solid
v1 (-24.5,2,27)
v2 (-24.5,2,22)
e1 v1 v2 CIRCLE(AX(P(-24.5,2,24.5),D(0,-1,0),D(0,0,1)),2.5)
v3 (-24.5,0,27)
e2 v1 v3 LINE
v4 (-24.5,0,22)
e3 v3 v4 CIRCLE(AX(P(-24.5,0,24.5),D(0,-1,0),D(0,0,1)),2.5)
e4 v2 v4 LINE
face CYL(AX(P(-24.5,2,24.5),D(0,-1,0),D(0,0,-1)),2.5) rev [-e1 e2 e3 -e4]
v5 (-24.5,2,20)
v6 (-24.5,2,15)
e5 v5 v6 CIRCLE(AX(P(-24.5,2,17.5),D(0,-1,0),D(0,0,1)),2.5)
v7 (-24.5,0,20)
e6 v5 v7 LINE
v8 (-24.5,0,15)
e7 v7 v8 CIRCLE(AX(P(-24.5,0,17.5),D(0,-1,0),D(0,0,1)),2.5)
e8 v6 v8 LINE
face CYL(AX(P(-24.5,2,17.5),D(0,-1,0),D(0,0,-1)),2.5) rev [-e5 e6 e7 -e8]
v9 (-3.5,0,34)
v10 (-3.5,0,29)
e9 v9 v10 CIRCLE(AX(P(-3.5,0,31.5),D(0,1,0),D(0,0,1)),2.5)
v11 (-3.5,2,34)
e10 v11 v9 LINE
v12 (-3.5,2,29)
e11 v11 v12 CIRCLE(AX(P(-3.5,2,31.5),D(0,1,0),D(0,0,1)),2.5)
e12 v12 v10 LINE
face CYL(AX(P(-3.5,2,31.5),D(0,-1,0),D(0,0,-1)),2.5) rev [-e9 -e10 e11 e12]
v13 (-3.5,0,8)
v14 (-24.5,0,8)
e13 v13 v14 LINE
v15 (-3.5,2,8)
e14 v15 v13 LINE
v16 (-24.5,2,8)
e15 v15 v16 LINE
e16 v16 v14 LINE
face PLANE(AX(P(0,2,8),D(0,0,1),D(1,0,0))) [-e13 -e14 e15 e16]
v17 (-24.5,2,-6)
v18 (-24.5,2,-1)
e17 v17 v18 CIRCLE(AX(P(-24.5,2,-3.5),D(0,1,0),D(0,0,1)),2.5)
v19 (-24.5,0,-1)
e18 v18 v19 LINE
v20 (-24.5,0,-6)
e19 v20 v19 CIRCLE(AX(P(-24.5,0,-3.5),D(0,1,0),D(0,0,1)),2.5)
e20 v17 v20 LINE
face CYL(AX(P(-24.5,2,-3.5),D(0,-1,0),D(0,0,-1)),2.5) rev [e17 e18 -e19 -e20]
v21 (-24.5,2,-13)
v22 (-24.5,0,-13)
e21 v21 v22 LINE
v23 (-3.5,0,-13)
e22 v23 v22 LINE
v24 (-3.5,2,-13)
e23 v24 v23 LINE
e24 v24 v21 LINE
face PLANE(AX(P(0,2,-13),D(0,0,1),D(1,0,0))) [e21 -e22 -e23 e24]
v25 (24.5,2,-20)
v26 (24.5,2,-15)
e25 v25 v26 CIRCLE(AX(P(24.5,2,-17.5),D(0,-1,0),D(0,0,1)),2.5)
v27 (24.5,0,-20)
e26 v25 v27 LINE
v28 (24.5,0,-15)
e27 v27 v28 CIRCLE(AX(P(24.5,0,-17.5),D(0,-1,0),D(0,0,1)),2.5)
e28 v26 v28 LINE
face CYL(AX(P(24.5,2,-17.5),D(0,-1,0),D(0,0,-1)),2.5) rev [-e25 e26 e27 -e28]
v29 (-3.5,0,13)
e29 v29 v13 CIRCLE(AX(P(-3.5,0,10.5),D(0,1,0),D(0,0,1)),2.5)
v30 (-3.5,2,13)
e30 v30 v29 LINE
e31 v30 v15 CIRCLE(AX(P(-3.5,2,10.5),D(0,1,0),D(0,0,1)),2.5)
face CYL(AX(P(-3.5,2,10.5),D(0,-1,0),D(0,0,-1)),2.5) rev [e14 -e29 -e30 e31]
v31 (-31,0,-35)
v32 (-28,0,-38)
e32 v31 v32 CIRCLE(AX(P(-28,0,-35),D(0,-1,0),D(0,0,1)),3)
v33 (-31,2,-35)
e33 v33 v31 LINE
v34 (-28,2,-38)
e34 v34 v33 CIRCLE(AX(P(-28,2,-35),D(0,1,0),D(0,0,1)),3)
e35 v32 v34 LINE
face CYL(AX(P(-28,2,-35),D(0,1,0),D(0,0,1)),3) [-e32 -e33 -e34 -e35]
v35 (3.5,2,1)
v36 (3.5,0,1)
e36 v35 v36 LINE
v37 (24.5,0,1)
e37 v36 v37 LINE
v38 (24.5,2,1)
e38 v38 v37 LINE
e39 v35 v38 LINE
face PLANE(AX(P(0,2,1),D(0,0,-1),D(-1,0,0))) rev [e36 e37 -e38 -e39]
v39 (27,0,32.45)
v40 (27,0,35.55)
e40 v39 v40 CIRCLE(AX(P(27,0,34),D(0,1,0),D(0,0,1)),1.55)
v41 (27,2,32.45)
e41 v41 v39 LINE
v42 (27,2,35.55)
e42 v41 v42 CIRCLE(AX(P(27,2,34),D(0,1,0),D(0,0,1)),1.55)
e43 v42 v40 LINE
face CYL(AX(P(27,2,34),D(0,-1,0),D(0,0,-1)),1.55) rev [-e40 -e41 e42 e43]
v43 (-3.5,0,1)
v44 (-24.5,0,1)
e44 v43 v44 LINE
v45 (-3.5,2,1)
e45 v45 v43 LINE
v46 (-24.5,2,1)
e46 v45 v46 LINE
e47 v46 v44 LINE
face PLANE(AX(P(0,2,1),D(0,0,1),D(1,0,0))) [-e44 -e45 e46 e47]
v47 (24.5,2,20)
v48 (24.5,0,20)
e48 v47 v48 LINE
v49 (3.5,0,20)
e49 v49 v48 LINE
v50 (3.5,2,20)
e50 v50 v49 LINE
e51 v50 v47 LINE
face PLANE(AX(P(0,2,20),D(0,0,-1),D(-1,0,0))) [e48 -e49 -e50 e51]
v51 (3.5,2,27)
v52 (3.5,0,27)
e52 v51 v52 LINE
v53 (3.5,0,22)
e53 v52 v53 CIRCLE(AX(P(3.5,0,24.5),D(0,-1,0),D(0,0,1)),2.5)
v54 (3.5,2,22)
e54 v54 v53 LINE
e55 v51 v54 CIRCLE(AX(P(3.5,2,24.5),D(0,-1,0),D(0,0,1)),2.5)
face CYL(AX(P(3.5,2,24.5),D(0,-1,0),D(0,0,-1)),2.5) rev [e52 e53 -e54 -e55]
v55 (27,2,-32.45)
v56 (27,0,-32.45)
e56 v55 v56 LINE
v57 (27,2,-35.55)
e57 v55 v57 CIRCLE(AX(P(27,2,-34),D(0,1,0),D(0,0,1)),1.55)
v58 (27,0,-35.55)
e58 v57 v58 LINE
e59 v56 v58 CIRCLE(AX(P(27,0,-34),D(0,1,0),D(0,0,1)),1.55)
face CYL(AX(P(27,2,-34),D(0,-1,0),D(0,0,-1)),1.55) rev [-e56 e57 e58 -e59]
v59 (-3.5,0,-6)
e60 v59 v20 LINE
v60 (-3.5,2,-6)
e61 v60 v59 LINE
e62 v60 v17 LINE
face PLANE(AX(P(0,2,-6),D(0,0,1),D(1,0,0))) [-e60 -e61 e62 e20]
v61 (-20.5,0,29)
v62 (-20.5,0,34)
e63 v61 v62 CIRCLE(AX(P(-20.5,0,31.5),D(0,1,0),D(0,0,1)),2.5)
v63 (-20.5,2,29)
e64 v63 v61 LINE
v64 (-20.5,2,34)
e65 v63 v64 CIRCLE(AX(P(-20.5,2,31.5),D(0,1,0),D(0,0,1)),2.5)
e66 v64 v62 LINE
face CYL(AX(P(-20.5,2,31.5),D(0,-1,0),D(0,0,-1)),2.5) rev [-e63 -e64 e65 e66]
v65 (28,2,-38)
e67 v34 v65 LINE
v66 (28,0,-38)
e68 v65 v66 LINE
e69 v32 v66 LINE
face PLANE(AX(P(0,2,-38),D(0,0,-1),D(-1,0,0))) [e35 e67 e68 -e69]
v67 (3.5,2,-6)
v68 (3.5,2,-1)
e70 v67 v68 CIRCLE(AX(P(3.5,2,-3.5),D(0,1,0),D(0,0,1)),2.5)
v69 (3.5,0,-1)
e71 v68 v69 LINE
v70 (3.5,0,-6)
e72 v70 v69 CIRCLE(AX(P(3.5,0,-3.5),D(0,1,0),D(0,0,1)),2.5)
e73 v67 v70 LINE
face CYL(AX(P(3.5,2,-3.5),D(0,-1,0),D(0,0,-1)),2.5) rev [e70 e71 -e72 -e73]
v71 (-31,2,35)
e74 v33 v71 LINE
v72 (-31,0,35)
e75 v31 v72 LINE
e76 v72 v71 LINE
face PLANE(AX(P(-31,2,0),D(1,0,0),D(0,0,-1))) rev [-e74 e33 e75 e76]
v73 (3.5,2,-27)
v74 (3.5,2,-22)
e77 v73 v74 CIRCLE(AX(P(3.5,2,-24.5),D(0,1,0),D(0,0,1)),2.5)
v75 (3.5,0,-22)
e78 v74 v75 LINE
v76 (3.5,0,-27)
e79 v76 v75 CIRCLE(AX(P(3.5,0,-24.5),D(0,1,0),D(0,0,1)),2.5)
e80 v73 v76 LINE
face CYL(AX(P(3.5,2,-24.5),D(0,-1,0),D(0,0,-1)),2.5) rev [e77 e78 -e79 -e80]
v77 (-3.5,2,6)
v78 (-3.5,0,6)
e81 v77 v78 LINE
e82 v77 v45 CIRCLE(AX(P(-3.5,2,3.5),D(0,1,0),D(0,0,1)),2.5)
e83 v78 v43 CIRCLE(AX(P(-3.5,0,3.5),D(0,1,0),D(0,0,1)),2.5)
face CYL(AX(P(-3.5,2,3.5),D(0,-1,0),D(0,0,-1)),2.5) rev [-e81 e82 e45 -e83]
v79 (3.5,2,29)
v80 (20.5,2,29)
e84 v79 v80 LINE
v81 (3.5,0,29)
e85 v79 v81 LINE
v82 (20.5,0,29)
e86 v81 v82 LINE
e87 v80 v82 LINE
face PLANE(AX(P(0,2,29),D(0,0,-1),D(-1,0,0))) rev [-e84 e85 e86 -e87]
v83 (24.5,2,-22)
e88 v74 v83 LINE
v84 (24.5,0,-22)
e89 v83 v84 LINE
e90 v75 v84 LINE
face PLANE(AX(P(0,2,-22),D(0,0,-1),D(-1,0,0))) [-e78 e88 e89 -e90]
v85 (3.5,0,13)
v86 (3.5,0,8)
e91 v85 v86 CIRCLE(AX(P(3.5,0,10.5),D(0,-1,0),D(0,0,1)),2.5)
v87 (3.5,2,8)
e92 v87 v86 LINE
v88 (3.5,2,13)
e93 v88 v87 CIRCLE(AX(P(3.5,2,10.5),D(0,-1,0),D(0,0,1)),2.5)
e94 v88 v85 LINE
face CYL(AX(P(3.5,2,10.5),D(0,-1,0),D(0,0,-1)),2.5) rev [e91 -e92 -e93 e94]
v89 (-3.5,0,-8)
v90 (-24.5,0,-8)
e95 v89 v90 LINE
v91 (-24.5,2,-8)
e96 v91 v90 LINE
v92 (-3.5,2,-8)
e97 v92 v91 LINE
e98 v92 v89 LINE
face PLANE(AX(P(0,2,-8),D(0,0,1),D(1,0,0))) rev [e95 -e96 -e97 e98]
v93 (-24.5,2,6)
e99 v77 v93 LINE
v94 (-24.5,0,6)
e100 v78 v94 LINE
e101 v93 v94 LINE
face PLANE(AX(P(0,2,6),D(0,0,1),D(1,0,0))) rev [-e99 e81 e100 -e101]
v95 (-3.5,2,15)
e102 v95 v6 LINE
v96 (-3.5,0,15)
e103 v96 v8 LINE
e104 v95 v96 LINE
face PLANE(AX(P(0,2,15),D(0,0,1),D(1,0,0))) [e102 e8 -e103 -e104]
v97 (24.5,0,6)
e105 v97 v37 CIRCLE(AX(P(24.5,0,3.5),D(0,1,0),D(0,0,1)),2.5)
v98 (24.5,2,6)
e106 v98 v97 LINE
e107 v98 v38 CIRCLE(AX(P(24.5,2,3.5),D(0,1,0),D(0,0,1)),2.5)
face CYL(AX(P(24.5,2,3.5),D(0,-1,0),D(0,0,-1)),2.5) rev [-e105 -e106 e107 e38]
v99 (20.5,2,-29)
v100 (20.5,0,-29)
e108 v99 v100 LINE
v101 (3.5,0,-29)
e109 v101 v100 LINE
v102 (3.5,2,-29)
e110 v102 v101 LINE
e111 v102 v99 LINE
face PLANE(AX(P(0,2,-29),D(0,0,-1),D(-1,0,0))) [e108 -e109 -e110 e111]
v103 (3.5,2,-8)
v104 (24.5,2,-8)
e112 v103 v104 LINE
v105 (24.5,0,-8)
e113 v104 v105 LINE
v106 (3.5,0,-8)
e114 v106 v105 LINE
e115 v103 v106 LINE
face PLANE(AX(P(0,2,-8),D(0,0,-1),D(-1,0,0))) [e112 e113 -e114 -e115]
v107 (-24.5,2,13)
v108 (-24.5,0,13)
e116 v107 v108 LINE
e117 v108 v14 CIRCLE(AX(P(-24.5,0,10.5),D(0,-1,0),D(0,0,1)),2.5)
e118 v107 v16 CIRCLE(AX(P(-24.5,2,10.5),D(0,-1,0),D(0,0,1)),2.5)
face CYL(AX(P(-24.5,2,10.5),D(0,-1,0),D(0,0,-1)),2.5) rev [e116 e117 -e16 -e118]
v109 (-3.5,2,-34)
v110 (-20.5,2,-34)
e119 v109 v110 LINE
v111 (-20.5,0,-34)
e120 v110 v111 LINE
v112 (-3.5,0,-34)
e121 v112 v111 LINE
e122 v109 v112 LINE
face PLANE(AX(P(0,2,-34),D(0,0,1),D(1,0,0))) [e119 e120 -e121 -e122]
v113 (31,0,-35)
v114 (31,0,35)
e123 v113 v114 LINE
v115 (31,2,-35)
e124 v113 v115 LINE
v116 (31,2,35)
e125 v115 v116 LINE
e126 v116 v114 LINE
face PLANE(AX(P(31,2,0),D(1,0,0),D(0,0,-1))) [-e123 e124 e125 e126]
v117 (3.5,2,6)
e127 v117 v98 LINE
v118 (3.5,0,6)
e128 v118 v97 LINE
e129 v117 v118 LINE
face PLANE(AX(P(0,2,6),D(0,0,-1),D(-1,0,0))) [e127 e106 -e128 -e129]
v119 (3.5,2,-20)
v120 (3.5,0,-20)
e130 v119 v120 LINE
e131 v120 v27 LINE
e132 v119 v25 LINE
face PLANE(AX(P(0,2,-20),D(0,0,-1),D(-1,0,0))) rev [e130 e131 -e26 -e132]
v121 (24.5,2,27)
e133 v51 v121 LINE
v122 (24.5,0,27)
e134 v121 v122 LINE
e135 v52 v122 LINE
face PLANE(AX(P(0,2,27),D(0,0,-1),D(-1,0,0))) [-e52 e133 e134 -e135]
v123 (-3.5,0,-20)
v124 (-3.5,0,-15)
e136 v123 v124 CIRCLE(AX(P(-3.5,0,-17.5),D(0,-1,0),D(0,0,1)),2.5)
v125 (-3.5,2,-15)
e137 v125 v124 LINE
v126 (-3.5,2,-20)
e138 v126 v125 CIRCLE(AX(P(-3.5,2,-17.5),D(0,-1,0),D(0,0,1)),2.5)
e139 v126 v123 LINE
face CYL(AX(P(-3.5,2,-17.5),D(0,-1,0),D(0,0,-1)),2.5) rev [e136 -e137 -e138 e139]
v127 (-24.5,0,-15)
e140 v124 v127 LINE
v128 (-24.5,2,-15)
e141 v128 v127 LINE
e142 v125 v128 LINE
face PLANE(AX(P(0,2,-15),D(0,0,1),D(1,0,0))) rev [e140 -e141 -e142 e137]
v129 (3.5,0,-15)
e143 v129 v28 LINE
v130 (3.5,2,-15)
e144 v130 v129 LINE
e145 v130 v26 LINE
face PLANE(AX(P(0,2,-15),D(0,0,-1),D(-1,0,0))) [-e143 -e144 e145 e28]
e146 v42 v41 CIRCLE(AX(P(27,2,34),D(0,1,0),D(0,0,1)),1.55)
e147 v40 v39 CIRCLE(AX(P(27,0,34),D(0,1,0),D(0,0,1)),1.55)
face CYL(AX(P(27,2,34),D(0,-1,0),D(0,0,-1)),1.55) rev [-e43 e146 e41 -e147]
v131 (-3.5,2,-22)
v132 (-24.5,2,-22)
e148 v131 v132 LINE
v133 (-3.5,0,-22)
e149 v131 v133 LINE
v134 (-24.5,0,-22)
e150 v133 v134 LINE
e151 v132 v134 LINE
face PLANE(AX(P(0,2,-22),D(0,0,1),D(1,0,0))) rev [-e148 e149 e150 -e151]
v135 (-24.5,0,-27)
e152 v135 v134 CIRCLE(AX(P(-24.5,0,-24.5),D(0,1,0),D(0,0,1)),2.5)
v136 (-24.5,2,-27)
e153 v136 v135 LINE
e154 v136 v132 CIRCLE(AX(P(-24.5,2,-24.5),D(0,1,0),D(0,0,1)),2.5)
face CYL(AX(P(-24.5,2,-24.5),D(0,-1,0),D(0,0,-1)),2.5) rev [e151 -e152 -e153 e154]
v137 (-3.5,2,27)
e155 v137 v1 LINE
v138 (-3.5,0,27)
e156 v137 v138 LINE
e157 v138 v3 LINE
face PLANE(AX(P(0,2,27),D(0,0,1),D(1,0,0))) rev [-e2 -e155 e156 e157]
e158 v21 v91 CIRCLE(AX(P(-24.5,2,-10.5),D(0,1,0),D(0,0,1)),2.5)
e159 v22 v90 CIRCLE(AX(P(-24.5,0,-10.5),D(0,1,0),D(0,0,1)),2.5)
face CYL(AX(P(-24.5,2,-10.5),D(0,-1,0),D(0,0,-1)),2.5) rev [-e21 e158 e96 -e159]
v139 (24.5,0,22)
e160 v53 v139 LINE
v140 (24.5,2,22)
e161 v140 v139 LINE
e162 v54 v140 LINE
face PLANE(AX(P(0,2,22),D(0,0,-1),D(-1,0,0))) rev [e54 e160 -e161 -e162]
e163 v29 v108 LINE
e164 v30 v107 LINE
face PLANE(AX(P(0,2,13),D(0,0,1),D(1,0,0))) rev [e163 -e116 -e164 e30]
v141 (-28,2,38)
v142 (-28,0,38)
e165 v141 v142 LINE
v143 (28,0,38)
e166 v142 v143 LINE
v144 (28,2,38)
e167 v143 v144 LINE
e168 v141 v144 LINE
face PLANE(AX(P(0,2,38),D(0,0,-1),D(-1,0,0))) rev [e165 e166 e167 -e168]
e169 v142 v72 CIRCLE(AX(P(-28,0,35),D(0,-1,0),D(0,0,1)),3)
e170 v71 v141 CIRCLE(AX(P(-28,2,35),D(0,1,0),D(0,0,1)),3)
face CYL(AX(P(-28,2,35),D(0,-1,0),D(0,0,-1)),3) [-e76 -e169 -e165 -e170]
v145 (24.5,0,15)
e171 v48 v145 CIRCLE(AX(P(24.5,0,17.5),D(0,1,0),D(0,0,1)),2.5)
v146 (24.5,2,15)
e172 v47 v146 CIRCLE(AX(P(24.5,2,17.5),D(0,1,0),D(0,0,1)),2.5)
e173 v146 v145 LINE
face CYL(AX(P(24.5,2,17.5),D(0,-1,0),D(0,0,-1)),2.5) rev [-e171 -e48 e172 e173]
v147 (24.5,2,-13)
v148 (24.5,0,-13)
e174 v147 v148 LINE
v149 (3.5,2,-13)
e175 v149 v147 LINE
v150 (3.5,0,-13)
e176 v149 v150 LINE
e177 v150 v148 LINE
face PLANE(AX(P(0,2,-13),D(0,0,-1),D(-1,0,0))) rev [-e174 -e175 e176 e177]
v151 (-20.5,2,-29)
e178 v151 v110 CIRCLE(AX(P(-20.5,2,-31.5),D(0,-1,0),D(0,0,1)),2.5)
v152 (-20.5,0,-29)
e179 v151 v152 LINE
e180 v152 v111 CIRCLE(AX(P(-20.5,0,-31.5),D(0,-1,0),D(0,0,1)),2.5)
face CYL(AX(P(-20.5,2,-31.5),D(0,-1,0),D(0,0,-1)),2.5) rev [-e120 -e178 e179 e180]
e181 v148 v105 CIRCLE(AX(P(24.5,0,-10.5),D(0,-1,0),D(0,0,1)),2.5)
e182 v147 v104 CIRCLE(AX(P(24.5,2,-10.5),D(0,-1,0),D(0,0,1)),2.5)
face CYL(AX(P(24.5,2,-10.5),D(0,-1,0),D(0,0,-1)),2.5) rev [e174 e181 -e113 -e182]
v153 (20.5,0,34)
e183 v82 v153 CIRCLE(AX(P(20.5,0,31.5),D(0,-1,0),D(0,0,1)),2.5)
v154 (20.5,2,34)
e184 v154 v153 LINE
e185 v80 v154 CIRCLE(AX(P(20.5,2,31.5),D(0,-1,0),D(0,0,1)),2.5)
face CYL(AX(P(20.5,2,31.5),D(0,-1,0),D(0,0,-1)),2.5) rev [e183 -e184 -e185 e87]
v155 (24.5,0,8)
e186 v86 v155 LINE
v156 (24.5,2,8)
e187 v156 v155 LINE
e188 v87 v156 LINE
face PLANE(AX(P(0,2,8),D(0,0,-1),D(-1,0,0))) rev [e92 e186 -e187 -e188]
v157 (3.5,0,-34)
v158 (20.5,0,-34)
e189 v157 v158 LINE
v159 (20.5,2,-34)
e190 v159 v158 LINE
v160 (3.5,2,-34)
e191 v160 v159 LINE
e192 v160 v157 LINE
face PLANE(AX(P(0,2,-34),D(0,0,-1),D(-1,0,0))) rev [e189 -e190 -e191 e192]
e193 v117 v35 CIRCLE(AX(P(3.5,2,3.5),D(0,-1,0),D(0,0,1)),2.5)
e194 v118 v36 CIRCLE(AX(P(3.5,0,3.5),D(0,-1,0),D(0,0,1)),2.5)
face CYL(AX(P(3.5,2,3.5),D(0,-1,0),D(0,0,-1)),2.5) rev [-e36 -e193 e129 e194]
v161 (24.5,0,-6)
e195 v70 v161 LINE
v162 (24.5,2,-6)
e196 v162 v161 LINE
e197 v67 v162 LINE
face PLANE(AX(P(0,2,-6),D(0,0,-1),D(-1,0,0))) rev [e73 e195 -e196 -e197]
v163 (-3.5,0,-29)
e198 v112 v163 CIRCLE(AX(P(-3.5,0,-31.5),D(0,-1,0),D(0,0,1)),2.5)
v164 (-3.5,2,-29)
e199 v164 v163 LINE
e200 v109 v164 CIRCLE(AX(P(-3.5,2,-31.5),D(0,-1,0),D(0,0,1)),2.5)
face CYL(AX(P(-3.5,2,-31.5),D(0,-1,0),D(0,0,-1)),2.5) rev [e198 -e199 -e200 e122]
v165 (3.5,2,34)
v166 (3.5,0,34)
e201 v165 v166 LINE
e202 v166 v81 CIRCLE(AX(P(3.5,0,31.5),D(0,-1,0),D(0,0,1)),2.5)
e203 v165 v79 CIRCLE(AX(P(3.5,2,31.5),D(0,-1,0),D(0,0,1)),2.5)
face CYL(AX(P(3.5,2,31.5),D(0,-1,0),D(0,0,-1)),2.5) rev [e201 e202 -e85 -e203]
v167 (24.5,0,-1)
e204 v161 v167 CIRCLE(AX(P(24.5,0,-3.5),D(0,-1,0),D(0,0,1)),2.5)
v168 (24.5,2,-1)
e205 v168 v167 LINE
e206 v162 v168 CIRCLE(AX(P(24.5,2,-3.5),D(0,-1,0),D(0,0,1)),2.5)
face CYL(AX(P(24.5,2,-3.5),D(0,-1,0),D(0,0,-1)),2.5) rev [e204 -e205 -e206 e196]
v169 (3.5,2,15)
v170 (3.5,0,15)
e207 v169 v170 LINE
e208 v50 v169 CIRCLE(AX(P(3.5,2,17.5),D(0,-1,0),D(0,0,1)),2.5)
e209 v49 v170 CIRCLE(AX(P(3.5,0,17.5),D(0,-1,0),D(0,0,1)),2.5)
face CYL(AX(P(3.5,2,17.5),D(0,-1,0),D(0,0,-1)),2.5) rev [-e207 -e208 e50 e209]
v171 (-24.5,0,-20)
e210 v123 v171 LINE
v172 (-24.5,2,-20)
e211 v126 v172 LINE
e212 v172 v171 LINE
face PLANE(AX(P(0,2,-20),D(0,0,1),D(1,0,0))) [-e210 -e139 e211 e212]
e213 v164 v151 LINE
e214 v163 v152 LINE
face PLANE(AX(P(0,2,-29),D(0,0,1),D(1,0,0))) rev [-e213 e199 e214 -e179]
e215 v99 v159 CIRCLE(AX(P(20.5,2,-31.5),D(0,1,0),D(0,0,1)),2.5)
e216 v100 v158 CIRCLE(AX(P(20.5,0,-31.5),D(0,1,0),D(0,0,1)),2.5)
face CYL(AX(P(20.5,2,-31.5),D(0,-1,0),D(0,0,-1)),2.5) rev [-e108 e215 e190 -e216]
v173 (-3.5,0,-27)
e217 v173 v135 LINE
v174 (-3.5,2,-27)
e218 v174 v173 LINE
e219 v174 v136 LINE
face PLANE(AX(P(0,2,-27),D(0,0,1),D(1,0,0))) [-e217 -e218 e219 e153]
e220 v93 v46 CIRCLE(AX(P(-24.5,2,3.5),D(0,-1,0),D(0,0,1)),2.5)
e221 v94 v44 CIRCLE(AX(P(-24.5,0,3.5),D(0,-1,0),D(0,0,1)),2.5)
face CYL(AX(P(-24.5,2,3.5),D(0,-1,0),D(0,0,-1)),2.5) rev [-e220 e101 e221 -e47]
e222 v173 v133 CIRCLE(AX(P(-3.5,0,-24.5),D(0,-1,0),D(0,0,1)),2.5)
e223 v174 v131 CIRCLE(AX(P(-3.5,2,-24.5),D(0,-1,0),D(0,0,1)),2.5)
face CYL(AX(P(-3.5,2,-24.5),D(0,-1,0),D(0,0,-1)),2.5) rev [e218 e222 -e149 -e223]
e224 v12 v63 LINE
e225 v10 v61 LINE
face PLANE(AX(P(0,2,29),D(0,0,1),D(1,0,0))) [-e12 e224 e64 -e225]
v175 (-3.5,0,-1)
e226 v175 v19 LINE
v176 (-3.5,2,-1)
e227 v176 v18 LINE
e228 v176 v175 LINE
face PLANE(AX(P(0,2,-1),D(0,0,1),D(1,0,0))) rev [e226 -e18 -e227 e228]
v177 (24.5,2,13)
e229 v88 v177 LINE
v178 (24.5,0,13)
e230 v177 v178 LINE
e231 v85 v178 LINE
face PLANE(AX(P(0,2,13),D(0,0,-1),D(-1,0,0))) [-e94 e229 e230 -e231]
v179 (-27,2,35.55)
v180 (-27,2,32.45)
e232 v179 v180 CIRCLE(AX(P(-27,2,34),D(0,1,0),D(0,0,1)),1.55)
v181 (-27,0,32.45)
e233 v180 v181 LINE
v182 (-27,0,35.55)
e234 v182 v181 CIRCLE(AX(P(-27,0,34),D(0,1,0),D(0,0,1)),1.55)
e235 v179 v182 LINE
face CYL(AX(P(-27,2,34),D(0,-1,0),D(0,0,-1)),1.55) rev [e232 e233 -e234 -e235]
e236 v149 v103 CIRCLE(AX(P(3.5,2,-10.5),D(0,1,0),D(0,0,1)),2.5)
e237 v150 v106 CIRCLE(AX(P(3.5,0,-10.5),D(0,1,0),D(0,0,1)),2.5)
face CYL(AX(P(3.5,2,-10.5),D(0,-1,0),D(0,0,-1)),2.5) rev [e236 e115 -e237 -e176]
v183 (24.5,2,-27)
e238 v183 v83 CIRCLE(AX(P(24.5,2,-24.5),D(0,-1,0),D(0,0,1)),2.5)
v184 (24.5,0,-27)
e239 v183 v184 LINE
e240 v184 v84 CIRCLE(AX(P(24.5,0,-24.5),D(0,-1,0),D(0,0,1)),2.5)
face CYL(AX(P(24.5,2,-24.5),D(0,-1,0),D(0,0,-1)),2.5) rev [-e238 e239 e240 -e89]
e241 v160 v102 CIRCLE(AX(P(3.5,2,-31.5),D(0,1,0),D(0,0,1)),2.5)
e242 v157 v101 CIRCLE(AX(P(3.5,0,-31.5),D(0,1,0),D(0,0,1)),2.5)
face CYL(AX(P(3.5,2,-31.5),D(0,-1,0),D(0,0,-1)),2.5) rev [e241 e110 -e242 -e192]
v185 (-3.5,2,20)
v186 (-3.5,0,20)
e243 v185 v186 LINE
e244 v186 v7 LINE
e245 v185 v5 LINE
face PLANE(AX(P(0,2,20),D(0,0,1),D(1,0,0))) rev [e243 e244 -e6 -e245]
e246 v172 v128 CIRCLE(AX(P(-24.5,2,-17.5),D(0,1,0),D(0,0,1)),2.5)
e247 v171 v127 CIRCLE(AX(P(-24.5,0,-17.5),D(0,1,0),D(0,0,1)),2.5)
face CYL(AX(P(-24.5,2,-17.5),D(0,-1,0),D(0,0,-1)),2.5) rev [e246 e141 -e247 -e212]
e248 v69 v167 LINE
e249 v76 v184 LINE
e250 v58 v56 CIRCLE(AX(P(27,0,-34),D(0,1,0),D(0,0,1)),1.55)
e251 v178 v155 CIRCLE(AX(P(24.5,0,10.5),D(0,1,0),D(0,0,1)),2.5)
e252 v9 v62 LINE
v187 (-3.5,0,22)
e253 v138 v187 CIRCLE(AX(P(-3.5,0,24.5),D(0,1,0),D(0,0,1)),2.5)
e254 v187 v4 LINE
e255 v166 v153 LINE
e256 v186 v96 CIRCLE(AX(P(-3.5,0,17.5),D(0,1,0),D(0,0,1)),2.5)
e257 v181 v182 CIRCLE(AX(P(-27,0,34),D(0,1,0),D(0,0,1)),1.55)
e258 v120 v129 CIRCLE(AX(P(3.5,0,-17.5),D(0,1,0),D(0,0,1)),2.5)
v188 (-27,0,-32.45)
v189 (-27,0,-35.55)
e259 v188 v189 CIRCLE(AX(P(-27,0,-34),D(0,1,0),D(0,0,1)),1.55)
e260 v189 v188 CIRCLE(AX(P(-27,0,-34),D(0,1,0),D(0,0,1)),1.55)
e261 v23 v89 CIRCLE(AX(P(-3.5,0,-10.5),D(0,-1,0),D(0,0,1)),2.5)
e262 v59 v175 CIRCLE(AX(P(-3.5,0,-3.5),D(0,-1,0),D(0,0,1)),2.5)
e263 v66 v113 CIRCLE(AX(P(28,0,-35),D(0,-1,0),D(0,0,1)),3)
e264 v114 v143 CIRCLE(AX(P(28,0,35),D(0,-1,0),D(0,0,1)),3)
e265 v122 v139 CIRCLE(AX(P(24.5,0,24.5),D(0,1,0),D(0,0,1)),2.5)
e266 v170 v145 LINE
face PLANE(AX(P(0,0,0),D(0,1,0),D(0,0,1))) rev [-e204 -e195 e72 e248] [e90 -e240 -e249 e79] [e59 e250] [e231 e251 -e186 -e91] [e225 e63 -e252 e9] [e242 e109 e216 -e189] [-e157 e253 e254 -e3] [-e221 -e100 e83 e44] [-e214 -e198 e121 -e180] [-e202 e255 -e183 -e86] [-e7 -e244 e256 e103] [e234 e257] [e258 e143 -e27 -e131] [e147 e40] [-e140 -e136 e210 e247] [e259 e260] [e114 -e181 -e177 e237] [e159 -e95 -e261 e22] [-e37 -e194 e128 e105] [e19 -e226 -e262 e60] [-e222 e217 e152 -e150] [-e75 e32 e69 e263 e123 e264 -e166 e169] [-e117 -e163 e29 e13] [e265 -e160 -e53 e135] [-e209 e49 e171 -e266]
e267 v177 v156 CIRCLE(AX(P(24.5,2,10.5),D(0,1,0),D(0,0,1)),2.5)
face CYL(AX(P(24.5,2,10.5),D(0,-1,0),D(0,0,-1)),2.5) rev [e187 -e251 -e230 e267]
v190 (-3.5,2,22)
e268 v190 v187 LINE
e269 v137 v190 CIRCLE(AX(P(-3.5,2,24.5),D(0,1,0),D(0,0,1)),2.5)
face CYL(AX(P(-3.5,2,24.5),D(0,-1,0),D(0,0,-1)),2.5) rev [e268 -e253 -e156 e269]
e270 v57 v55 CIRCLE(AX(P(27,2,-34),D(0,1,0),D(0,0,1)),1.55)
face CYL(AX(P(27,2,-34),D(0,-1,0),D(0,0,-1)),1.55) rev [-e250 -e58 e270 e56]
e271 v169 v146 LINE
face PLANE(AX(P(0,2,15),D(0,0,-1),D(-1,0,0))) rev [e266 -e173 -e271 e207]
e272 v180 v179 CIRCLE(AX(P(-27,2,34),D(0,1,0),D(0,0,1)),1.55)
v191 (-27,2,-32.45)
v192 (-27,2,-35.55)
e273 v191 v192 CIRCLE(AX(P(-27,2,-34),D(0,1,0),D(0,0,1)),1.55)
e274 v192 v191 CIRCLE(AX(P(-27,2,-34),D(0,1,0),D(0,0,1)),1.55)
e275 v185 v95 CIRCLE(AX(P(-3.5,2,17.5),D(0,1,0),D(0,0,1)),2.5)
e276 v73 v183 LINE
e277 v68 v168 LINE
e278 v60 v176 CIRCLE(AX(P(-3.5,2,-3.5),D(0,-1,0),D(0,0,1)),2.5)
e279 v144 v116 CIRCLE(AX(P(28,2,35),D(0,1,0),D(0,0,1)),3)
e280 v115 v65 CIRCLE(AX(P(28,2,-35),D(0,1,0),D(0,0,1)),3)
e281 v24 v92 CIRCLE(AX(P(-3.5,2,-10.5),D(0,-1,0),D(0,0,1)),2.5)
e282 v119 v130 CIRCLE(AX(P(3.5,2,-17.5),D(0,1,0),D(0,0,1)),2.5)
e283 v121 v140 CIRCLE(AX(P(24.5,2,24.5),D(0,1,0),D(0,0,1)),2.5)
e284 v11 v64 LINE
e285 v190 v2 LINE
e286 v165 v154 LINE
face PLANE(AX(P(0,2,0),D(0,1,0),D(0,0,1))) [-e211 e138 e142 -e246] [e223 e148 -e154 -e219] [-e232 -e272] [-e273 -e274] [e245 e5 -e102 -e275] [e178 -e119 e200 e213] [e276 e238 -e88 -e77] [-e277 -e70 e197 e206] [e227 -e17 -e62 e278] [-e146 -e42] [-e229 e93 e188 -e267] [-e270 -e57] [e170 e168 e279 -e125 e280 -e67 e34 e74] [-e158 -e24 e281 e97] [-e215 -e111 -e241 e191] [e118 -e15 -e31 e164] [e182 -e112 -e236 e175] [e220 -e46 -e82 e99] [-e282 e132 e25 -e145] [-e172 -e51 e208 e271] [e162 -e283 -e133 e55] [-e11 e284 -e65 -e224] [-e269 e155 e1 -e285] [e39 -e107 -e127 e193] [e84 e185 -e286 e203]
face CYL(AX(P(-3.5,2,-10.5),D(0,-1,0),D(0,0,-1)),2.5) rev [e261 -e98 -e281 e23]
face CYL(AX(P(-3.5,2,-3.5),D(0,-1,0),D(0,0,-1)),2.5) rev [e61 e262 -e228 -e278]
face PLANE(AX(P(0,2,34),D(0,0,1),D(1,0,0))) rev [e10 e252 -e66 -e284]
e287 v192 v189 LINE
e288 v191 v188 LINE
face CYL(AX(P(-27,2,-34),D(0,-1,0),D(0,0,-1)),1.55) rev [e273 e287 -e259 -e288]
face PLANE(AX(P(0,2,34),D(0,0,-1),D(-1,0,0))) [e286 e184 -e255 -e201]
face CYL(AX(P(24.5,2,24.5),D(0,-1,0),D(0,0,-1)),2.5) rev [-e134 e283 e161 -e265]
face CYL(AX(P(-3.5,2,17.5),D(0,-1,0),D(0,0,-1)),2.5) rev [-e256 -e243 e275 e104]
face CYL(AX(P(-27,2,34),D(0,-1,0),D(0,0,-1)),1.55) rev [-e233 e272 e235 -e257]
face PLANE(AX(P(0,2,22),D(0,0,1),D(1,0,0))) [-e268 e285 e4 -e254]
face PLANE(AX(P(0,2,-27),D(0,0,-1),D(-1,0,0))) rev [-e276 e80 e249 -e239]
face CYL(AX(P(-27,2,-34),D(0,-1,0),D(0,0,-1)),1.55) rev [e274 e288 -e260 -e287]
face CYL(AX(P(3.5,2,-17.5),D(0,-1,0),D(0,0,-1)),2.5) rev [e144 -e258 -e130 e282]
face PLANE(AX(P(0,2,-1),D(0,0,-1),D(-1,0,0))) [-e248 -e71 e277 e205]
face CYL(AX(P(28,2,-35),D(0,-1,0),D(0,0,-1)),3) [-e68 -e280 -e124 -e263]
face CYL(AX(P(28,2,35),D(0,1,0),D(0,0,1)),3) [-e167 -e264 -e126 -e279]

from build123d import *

# Parameters (mm, degrees)
SKETCH_1_W      = 62
SKETCH_1_H      = 76
SKETCH_1_R      = 1.55
EXTRUDE_1_DEPTH = 2
FILLET_1_R      = 3


with BuildPart() as part:
    # 草图1 → 凸台-拉伸1 (new body)
    with BuildSketch(Plane(origin=(0, 0, 0), x_dir=(1, 0, 0), z_dir=(0, 1, 0))):
        Rectangle(SKETCH_1_W, SKETCH_1_H)
        with Locations(Location((-27, -34, 0), (0, 0, 270))):
            Circle(SKETCH_1_R, mode=Mode.SUBTRACT)
        with BuildLine():
            ThreePointArc((-3.5, -29), (-1, -31.5), (-3.5, -34))
            Line((-3.5, -34), (-20.5, -34))
            ThreePointArc((-20.5, -34), (-23, -31.5), (-20.5, -29))
            Line((-20.5, -29), (-3.5, -29))
        make_face(mode=Mode.SUBTRACT)
        with BuildLine():
            ThreePointArc((-3.5, -22), (-1, -24.5), (-3.5, -27))
            Line((-3.5, -27), (-20.5, -27))
            Line((-20.5, -27), (-24.5, -27))
            ThreePointArc((-24.5, -27), (-27, -24.5), (-24.5, -22))
            Line((-24.5, -22), (-20.5, -22))
            Line((-20.5, -22), (-3.5, -22))
        make_face(mode=Mode.SUBTRACT)
        with BuildLine():
            ThreePointArc((-3.5, -15), (-1, -17.5), (-3.5, -20))
            Line((-3.5, -20), (-20.5, -20))
            Line((-20.5, -20), (-24.5, -20))
            ThreePointArc((-24.5, -20), (-27, -17.5), (-24.5, -15))
            Line((-24.5, -15), (-20.5, -15))
            Line((-20.5, -15), (-3.5, -15))
        make_face(mode=Mode.SUBTRACT)
        with BuildLine():
            ThreePointArc((-3.5, -8), (-1, -10.5), (-3.5, -13))
            Line((-3.5, -13), (-20.5, -13))
            Line((-20.5, -13), (-24.5, -13))
            ThreePointArc((-24.5, -13), (-27, -10.5), (-24.5, -8))
            Line((-24.5, -8), (-20.5, -8))
            Line((-20.5, -8), (-3.5, -8))
        make_face(mode=Mode.SUBTRACT)
        with BuildLine():
            ThreePointArc((-3.5, -1), (-1, -3.5), (-3.5, -6))
            Line((-3.5, -6), (-20.5, -6))
            Line((-20.5, -6), (-24.5, -6))
            ThreePointArc((-24.5, -6), (-27, -3.5), (-24.5, -1))
            Line((-24.5, -1), (-20.5, -1))
            Line((-20.5, -1), (-3.5, -1))
        make_face(mode=Mode.SUBTRACT)
        with BuildLine():
            Line((20.5, -34), (3.5, -34))
            ThreePointArc((3.5, -34), (1, -31.5), (3.5, -29))
            Line((3.5, -29), (20.5, -29))
            ThreePointArc((20.5, -29), (23, -31.5), (20.5, -34))
        make_face(mode=Mode.SUBTRACT)
        with BuildLine():
            Line((20.5, -27), (3.5, -27))
            ThreePointArc((3.5, -27), (1, -24.5), (3.5, -22))
            Line((3.5, -22), (20.5, -22))
            Line((20.5, -22), (24.5, -22))
            ThreePointArc((24.5, -22), (27, -24.5), (24.5, -27))
            Line((24.5, -27), (20.5, -27))
        make_face(mode=Mode.SUBTRACT)
        with Locations(Location((27, -34, 0), (0, 0, 270))):
            Circle(SKETCH_1_R, mode=Mode.SUBTRACT)
        with BuildLine():
            Line((20.5, -20), (3.5, -20))
            ThreePointArc((3.5, -20), (1, -17.5), (3.5, -15))
            Line((3.5, -15), (20.5, -15))
            Line((20.5, -15), (24.5, -15))
            ThreePointArc((24.5, -15), (27, -17.5), (24.5, -20))
            Line((24.5, -20), (20.5, -20))
        make_face(mode=Mode.SUBTRACT)
        with BuildLine():
            Line((20.5, -13), (3.5, -13))
            ThreePointArc((3.5, -13), (1, -10.5), (3.5, -8))
            Line((3.5, -8), (20.5, -8))
            Line((20.5, -8), (24.5, -8))
            ThreePointArc((24.5, -8), (27, -10.5), (24.5, -13))
            Line((24.5, -13), (20.5, -13))
        make_face(mode=Mode.SUBTRACT)
        with BuildLine():
            Line((20.5, -6), (3.5, -6))
            ThreePointArc((3.5, -6), (1, -3.5), (3.5, -1))
            Line((3.5, -1), (20.5, -1))
            Line((20.5, -1), (24.5, -1))
            ThreePointArc((24.5, -1), (27, -3.5), (24.5, -6))
            Line((24.5, -6), (20.5, -6))
        make_face(mode=Mode.SUBTRACT)
        with BuildLine():
            Line((-20.5, 6), (-3.5, 6))
            ThreePointArc((-3.5, 6), (-1, 3.5), (-3.5, 1))
            Line((-3.5, 1), (-20.5, 1))
            Line((-20.5, 1), (-24.5, 1))
            ThreePointArc((-24.5, 1), (-27, 3.5), (-24.5, 6))
            Line((-24.5, 6), (-20.5, 6))
        make_face(mode=Mode.SUBTRACT)
        with BuildLine():
            Line((-20.5, 13), (-3.5, 13))
            ThreePointArc((-3.5, 13), (-1, 10.5), (-3.5, 8))
            Line((-3.5, 8), (-20.5, 8))
            Line((-20.5, 8), (-24.5, 8))
            ThreePointArc((-24.5, 8), (-27, 10.5), (-24.5, 13))
            Line((-24.5, 13), (-20.5, 13))
        make_face(mode=Mode.SUBTRACT)
        with BuildLine():
            Line((-20.5, 20), (-3.5, 20))
            ThreePointArc((-3.5, 20), (-1, 17.5), (-3.5, 15))
            Line((-3.5, 15), (-20.5, 15))
            Line((-20.5, 15), (-24.5, 15))
            ThreePointArc((-24.5, 15), (-27, 17.5), (-24.5, 20))
            Line((-24.5, 20), (-20.5, 20))
        make_face(mode=Mode.SUBTRACT)
        with Locations(Location((-27, 34, 0), (0, 0, 270))):
            Circle(SKETCH_1_R, mode=Mode.SUBTRACT)
        with BuildLine():
            Line((-20.5, 27), (-3.5, 27))
            ThreePointArc((-3.5, 27), (-1, 24.5), (-3.5, 22))
            Line((-3.5, 22), (-20.5, 22))
            Line((-20.5, 22), (-24.5, 22))
            ThreePointArc((-24.5, 22), (-27, 24.5), (-24.5, 27))
            Line((-24.5, 27), (-20.5, 27))
        make_face(mode=Mode.SUBTRACT)
        with BuildLine():
            Line((-20.5, 34), (-3.5, 34))
            ThreePointArc((-3.5, 34), (-1, 31.5), (-3.5, 29))
            Line((-3.5, 29), (-20.5, 29))
            ThreePointArc((-20.5, 29), (-23, 31.5), (-20.5, 34))
        make_face(mode=Mode.SUBTRACT)
        with BuildLine():
            ThreePointArc((3.5, 1), (1, 3.5), (3.5, 6))
            Line((3.5, 6), (20.5, 6))
            Line((20.5, 6), (24.5, 6))
            ThreePointArc((24.5, 6), (27, 3.5), (24.5, 1))
            Line((24.5, 1), (20.5, 1))
            Line((20.5, 1), (3.5, 1))
        make_face(mode=Mode.SUBTRACT)
        with BuildLine():
            ThreePointArc((3.5, 8), (1, 10.5), (3.5, 13))
            Line((3.5, 13), (20.5, 13))
            Line((20.5, 13), (24.5, 13))
            ThreePointArc((24.5, 13), (27, 10.5), (24.5, 8))
            Line((24.5, 8), (20.5, 8))
            Line((20.5, 8), (3.5, 8))
        make_face(mode=Mode.SUBTRACT)
        with BuildLine():
            ThreePointArc((3.5, 15), (1, 17.5), (3.5, 20))
            Line((3.5, 20), (20.5, 20))
            Line((20.5, 20), (24.5, 20))
            ThreePointArc((24.5, 20), (27, 17.5), (24.5, 15))
            Line((24.5, 15), (20.5, 15))
            Line((20.5, 15), (3.5, 15))
        make_face(mode=Mode.SUBTRACT)
        with BuildLine():
            ThreePointArc((3.5, 22), (1, 24.5), (3.5, 27))
            Line((3.5, 27), (20.5, 27))
            Line((20.5, 27), (24.5, 27))
            ThreePointArc((24.5, 27), (27, 24.5), (24.5, 22))
            Line((24.5, 22), (20.5, 22))
            Line((20.5, 22), (3.5, 22))
        make_face(mode=Mode.SUBTRACT)
        with BuildLine():
            ThreePointArc((3.5, 29), (1, 31.5), (3.5, 34))
            Line((3.5, 34), (20.5, 34))
            ThreePointArc((20.5, 34), (23, 31.5), (20.5, 29))
            Line((20.5, 29), (3.5, 29))
        make_face(mode=Mode.SUBTRACT)
        with Locations(Location((27, 34, 0), (0, 0, 270))):
            Circle(SKETCH_1_R, mode=Mode.SUBTRACT)
    extrude(amount=EXTRUDE_1_DEPTH)

    # 圆角1
    fillet_1_edges = [part.edges().sort_by_distance(p)[0] for p in [
        (31, 1, -38),
        (31, 1, 38),
        (-31, 1, 38),
        (-31, 1, -38),
    ]]
    fillet(fillet_1_edges, radius=FILLET_1_R)


solid = part.part
